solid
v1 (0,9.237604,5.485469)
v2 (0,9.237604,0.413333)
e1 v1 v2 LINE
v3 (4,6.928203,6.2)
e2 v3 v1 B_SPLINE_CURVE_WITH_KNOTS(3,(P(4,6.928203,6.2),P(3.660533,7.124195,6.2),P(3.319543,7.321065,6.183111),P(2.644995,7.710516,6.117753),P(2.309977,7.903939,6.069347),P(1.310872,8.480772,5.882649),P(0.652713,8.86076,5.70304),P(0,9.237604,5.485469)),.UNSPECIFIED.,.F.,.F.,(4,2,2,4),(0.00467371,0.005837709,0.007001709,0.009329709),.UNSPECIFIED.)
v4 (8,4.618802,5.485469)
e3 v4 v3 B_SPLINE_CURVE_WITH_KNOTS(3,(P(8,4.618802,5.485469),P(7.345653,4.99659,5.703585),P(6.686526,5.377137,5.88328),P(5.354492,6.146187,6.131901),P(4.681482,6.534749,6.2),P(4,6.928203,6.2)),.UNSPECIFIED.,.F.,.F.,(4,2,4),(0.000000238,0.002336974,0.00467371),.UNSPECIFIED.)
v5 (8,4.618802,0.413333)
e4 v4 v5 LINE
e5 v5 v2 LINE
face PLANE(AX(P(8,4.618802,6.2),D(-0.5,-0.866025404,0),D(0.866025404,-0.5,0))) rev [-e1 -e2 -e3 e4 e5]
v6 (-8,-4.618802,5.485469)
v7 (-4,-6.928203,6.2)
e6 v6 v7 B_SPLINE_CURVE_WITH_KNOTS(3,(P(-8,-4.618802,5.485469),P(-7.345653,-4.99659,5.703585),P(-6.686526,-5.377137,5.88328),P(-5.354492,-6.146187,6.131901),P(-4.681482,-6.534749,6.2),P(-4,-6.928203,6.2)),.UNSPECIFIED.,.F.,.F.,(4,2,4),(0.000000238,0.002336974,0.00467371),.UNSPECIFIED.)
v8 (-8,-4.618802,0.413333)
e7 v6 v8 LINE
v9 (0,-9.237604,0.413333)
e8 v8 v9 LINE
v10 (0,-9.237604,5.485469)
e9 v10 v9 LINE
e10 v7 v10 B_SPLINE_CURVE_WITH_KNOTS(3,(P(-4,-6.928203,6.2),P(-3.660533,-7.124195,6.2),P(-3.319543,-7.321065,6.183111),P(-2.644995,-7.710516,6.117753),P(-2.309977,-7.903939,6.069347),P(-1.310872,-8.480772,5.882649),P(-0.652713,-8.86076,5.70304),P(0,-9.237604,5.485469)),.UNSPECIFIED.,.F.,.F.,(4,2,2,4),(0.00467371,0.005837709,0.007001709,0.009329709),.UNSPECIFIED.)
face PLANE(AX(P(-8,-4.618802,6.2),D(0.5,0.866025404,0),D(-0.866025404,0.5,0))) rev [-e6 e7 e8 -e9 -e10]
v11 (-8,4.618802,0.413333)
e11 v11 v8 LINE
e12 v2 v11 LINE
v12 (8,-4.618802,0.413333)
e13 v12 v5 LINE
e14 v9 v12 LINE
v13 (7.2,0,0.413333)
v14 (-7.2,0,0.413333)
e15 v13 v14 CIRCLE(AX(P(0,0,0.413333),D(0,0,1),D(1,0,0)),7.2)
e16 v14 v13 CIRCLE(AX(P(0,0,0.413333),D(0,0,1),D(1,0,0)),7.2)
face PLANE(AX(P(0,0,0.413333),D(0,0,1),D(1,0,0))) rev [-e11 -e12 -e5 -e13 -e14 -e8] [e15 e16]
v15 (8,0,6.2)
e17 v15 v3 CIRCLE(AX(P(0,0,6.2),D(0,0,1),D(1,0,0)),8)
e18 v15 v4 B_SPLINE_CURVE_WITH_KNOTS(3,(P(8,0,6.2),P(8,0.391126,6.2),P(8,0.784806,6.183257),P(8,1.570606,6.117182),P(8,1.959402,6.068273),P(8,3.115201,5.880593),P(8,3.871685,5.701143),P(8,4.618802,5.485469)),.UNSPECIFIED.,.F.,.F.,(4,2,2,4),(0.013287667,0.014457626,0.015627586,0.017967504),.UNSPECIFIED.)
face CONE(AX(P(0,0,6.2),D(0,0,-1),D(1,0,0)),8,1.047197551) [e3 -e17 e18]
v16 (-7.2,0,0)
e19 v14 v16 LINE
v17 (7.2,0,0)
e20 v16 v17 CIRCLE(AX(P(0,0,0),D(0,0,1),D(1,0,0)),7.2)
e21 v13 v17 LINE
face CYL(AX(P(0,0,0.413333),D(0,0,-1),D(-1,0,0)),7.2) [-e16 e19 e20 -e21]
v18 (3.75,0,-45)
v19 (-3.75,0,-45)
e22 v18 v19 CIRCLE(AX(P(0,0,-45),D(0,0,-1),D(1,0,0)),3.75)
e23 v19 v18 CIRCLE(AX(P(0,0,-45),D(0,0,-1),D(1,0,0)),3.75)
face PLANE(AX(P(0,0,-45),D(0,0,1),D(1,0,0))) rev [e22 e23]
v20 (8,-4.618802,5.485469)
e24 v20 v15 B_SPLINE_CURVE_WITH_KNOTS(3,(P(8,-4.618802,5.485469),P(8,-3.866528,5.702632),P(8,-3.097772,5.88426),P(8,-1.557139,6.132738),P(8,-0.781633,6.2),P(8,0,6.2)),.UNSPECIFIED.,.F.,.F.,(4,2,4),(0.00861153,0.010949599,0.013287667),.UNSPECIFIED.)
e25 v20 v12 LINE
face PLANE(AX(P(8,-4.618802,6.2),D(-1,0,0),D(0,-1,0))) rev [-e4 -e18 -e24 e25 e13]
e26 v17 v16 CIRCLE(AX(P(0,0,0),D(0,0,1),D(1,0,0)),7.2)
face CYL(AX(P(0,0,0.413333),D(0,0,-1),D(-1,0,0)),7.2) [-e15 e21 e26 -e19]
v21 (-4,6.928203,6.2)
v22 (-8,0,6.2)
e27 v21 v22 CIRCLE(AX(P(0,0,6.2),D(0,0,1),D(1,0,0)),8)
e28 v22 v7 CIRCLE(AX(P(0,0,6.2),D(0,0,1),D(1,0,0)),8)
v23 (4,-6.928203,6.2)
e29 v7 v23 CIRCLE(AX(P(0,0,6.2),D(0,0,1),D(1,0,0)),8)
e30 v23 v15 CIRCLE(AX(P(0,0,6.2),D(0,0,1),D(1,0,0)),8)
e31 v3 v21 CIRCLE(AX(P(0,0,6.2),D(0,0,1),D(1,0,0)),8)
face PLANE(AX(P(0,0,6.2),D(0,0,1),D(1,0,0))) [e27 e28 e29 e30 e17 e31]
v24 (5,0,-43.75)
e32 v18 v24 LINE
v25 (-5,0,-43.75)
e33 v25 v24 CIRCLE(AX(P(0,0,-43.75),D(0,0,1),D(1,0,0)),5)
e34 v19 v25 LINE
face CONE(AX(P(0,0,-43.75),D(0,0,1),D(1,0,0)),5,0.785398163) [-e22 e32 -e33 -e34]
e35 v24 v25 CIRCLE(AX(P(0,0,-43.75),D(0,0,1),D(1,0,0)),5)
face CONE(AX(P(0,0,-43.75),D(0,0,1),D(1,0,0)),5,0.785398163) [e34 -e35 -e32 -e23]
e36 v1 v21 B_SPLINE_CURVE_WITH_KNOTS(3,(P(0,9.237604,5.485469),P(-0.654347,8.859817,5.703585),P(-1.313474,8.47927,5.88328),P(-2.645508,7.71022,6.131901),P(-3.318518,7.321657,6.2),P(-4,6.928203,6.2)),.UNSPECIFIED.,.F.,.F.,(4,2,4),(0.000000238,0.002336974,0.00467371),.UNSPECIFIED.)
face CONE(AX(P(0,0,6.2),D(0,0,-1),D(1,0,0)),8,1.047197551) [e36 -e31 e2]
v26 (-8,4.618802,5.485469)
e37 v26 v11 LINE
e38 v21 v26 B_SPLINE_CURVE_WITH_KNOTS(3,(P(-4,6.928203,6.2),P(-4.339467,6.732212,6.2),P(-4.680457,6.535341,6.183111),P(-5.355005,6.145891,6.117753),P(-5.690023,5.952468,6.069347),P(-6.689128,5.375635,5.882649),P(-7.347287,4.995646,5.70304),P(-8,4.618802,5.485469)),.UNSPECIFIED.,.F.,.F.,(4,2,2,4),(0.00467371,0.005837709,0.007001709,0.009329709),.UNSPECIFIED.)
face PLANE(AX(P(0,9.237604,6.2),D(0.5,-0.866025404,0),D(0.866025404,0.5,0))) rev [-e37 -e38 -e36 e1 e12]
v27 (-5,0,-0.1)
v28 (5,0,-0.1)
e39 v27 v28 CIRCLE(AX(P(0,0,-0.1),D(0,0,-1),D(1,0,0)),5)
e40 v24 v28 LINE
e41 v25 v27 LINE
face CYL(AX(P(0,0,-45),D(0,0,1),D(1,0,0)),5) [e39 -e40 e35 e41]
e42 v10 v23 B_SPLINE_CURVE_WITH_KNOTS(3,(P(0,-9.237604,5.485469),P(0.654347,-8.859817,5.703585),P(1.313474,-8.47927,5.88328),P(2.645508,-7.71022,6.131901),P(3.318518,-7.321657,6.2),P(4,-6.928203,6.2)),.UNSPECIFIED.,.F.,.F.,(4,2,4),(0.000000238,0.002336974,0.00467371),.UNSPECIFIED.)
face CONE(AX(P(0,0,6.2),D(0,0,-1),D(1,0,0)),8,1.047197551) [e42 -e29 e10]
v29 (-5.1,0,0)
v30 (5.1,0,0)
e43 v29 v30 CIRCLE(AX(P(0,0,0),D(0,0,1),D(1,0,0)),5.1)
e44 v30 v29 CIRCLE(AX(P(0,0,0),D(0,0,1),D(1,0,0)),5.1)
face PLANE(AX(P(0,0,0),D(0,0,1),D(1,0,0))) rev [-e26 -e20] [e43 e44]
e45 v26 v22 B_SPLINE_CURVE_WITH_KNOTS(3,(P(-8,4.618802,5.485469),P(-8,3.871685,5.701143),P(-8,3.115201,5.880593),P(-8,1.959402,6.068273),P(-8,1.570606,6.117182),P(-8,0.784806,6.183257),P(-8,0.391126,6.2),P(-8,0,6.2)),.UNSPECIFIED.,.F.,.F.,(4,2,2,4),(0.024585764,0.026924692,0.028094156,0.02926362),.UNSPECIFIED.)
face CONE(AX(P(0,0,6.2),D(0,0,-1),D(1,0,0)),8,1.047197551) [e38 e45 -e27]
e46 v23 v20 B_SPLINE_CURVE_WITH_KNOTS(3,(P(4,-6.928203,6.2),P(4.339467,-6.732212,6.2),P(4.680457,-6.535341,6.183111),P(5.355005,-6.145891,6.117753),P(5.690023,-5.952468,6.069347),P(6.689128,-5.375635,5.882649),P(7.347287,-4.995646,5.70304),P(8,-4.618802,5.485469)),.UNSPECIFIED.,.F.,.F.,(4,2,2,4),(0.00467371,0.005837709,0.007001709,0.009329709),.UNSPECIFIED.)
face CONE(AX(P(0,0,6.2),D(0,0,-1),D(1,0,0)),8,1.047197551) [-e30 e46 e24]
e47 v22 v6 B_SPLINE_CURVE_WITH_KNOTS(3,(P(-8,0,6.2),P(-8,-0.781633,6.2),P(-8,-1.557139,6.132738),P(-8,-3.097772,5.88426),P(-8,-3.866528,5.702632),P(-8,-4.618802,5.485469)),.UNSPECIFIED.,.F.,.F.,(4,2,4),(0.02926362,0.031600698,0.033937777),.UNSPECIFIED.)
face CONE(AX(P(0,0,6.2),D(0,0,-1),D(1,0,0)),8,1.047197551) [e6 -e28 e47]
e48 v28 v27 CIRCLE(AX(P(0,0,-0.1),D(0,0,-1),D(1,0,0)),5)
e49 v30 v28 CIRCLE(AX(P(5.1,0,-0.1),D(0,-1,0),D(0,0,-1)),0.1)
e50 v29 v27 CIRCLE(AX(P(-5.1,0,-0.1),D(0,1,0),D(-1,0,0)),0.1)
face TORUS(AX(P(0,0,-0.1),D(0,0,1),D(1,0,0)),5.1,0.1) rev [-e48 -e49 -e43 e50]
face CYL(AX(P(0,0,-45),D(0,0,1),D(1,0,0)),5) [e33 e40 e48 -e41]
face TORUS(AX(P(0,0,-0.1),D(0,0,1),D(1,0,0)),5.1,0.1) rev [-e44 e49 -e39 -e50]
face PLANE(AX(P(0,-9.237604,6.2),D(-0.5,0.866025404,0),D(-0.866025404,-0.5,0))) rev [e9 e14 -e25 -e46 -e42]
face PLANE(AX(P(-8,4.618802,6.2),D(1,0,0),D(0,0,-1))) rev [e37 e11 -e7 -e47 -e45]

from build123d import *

# Parameters (mm, degrees)
EXTRUDE_1_DEPTH     = 6.2
SKETCH_3_R          = 5
EXTRUDE_3_DEPTH     = 45
SKETCH_5_OUTSIDE_W  = 375.758
SKETCH_5_OUTSIDE_H  = 378.234
SKETCH_5_OUTSIDE_R  = 8
CUT_EXTRUDE_2_DEPTH = 100
CUT_EXTRUDE_2_DRAFT = -60
CHAMFER_1_SIZE      = 1.25
SKETCH_2_OUTSIDE_W  = 29.346
SKETCH_2_OUTSIDE_H  = 31.822
SKETCH_2_OUTSIDE_R  = 7.2
CUT_EXTRUDE_1_DEPTH = 0.413333333
FILLET_1_R          = 0.1


with BuildPart() as part:
    # 草图1 → 凸台-拉伸1 (new body)
    with BuildSketch(Plane.XY):
        Polygon((0, 9.237604307), (-8, 4.618802154), (-8, -4.618802154), (0, -9.237604307), (8, -4.618802154), (8, 4.618802154), align=None)
    extrude(amount=EXTRUDE_1_DEPTH)

    # 草图3 → 凸台-拉伸3 (add)
    with BuildSketch(Plane.XY):
        Circle(SKETCH_3_R)
    extrude(amount=-EXTRUDE_3_DEPTH)


with BuildPart() as cut_extrude_2_tool:
    # 草图5 outside → 切除-拉伸2 (with draft: the straight prism first)
    with BuildSketch(Plane.XY.offset(6.2)):
        Rectangle(SKETCH_5_OUTSIDE_W, SKETCH_5_OUTSIDE_H)
        Circle(SKETCH_5_OUTSIDE_R, mode=Mode.SUBTRACT)
    extrude(amount=-CUT_EXTRUDE_2_DEPTH)
    # 切除-拉伸2: the draft: its side faces are tilted about the plane it starts from
    cut_extrude_2_sides = [cut_extrude_2_tool.faces().sort_by_distance(p)[0] for p in [
        (0, -189.117, -43.8),
        (187.879, 0, -43.8),
        (0, 189.117, -43.8),
        (-187.879, 0, -43.8),
        (-8, 0, -43.8),
    ]]
    draft(cut_extrude_2_sides, Plane.XY.offset(6.2), CUT_EXTRUDE_2_DRAFT)


with BuildPart() as part_1:
    add(part.part)

    # 切除-拉伸2: cut by cut_extrude_2_tool
    add(cut_extrude_2_tool.part, mode=Mode.SUBTRACT)

    # 倒角1
    chamfer_1_edges = [part_1.edges().sort_by_distance(p)[0] for p in [
        (-5, 0, -45),
    ]]
    chamfer(chamfer_1_edges, length=CHAMFER_1_SIZE)

    # 草图2 outside → 切除-拉伸1 (cut)
    with BuildSketch(Plane.XY):
        Rectangle(SKETCH_2_OUTSIDE_W, SKETCH_2_OUTSIDE_H)
        Circle(SKETCH_2_OUTSIDE_R, mode=Mode.SUBTRACT)
    extrude(amount=CUT_EXTRUDE_1_DEPTH, mode=Mode.SUBTRACT)

    # 圆角1
    fillet_1_edges = [part_1.edges().sort_by_distance(p)[0] for p in [
        (-5, 0, 0),
    ]]
    fillet(fillet_1_edges, radius=FILLET_1_R)


solid = part_1.part
